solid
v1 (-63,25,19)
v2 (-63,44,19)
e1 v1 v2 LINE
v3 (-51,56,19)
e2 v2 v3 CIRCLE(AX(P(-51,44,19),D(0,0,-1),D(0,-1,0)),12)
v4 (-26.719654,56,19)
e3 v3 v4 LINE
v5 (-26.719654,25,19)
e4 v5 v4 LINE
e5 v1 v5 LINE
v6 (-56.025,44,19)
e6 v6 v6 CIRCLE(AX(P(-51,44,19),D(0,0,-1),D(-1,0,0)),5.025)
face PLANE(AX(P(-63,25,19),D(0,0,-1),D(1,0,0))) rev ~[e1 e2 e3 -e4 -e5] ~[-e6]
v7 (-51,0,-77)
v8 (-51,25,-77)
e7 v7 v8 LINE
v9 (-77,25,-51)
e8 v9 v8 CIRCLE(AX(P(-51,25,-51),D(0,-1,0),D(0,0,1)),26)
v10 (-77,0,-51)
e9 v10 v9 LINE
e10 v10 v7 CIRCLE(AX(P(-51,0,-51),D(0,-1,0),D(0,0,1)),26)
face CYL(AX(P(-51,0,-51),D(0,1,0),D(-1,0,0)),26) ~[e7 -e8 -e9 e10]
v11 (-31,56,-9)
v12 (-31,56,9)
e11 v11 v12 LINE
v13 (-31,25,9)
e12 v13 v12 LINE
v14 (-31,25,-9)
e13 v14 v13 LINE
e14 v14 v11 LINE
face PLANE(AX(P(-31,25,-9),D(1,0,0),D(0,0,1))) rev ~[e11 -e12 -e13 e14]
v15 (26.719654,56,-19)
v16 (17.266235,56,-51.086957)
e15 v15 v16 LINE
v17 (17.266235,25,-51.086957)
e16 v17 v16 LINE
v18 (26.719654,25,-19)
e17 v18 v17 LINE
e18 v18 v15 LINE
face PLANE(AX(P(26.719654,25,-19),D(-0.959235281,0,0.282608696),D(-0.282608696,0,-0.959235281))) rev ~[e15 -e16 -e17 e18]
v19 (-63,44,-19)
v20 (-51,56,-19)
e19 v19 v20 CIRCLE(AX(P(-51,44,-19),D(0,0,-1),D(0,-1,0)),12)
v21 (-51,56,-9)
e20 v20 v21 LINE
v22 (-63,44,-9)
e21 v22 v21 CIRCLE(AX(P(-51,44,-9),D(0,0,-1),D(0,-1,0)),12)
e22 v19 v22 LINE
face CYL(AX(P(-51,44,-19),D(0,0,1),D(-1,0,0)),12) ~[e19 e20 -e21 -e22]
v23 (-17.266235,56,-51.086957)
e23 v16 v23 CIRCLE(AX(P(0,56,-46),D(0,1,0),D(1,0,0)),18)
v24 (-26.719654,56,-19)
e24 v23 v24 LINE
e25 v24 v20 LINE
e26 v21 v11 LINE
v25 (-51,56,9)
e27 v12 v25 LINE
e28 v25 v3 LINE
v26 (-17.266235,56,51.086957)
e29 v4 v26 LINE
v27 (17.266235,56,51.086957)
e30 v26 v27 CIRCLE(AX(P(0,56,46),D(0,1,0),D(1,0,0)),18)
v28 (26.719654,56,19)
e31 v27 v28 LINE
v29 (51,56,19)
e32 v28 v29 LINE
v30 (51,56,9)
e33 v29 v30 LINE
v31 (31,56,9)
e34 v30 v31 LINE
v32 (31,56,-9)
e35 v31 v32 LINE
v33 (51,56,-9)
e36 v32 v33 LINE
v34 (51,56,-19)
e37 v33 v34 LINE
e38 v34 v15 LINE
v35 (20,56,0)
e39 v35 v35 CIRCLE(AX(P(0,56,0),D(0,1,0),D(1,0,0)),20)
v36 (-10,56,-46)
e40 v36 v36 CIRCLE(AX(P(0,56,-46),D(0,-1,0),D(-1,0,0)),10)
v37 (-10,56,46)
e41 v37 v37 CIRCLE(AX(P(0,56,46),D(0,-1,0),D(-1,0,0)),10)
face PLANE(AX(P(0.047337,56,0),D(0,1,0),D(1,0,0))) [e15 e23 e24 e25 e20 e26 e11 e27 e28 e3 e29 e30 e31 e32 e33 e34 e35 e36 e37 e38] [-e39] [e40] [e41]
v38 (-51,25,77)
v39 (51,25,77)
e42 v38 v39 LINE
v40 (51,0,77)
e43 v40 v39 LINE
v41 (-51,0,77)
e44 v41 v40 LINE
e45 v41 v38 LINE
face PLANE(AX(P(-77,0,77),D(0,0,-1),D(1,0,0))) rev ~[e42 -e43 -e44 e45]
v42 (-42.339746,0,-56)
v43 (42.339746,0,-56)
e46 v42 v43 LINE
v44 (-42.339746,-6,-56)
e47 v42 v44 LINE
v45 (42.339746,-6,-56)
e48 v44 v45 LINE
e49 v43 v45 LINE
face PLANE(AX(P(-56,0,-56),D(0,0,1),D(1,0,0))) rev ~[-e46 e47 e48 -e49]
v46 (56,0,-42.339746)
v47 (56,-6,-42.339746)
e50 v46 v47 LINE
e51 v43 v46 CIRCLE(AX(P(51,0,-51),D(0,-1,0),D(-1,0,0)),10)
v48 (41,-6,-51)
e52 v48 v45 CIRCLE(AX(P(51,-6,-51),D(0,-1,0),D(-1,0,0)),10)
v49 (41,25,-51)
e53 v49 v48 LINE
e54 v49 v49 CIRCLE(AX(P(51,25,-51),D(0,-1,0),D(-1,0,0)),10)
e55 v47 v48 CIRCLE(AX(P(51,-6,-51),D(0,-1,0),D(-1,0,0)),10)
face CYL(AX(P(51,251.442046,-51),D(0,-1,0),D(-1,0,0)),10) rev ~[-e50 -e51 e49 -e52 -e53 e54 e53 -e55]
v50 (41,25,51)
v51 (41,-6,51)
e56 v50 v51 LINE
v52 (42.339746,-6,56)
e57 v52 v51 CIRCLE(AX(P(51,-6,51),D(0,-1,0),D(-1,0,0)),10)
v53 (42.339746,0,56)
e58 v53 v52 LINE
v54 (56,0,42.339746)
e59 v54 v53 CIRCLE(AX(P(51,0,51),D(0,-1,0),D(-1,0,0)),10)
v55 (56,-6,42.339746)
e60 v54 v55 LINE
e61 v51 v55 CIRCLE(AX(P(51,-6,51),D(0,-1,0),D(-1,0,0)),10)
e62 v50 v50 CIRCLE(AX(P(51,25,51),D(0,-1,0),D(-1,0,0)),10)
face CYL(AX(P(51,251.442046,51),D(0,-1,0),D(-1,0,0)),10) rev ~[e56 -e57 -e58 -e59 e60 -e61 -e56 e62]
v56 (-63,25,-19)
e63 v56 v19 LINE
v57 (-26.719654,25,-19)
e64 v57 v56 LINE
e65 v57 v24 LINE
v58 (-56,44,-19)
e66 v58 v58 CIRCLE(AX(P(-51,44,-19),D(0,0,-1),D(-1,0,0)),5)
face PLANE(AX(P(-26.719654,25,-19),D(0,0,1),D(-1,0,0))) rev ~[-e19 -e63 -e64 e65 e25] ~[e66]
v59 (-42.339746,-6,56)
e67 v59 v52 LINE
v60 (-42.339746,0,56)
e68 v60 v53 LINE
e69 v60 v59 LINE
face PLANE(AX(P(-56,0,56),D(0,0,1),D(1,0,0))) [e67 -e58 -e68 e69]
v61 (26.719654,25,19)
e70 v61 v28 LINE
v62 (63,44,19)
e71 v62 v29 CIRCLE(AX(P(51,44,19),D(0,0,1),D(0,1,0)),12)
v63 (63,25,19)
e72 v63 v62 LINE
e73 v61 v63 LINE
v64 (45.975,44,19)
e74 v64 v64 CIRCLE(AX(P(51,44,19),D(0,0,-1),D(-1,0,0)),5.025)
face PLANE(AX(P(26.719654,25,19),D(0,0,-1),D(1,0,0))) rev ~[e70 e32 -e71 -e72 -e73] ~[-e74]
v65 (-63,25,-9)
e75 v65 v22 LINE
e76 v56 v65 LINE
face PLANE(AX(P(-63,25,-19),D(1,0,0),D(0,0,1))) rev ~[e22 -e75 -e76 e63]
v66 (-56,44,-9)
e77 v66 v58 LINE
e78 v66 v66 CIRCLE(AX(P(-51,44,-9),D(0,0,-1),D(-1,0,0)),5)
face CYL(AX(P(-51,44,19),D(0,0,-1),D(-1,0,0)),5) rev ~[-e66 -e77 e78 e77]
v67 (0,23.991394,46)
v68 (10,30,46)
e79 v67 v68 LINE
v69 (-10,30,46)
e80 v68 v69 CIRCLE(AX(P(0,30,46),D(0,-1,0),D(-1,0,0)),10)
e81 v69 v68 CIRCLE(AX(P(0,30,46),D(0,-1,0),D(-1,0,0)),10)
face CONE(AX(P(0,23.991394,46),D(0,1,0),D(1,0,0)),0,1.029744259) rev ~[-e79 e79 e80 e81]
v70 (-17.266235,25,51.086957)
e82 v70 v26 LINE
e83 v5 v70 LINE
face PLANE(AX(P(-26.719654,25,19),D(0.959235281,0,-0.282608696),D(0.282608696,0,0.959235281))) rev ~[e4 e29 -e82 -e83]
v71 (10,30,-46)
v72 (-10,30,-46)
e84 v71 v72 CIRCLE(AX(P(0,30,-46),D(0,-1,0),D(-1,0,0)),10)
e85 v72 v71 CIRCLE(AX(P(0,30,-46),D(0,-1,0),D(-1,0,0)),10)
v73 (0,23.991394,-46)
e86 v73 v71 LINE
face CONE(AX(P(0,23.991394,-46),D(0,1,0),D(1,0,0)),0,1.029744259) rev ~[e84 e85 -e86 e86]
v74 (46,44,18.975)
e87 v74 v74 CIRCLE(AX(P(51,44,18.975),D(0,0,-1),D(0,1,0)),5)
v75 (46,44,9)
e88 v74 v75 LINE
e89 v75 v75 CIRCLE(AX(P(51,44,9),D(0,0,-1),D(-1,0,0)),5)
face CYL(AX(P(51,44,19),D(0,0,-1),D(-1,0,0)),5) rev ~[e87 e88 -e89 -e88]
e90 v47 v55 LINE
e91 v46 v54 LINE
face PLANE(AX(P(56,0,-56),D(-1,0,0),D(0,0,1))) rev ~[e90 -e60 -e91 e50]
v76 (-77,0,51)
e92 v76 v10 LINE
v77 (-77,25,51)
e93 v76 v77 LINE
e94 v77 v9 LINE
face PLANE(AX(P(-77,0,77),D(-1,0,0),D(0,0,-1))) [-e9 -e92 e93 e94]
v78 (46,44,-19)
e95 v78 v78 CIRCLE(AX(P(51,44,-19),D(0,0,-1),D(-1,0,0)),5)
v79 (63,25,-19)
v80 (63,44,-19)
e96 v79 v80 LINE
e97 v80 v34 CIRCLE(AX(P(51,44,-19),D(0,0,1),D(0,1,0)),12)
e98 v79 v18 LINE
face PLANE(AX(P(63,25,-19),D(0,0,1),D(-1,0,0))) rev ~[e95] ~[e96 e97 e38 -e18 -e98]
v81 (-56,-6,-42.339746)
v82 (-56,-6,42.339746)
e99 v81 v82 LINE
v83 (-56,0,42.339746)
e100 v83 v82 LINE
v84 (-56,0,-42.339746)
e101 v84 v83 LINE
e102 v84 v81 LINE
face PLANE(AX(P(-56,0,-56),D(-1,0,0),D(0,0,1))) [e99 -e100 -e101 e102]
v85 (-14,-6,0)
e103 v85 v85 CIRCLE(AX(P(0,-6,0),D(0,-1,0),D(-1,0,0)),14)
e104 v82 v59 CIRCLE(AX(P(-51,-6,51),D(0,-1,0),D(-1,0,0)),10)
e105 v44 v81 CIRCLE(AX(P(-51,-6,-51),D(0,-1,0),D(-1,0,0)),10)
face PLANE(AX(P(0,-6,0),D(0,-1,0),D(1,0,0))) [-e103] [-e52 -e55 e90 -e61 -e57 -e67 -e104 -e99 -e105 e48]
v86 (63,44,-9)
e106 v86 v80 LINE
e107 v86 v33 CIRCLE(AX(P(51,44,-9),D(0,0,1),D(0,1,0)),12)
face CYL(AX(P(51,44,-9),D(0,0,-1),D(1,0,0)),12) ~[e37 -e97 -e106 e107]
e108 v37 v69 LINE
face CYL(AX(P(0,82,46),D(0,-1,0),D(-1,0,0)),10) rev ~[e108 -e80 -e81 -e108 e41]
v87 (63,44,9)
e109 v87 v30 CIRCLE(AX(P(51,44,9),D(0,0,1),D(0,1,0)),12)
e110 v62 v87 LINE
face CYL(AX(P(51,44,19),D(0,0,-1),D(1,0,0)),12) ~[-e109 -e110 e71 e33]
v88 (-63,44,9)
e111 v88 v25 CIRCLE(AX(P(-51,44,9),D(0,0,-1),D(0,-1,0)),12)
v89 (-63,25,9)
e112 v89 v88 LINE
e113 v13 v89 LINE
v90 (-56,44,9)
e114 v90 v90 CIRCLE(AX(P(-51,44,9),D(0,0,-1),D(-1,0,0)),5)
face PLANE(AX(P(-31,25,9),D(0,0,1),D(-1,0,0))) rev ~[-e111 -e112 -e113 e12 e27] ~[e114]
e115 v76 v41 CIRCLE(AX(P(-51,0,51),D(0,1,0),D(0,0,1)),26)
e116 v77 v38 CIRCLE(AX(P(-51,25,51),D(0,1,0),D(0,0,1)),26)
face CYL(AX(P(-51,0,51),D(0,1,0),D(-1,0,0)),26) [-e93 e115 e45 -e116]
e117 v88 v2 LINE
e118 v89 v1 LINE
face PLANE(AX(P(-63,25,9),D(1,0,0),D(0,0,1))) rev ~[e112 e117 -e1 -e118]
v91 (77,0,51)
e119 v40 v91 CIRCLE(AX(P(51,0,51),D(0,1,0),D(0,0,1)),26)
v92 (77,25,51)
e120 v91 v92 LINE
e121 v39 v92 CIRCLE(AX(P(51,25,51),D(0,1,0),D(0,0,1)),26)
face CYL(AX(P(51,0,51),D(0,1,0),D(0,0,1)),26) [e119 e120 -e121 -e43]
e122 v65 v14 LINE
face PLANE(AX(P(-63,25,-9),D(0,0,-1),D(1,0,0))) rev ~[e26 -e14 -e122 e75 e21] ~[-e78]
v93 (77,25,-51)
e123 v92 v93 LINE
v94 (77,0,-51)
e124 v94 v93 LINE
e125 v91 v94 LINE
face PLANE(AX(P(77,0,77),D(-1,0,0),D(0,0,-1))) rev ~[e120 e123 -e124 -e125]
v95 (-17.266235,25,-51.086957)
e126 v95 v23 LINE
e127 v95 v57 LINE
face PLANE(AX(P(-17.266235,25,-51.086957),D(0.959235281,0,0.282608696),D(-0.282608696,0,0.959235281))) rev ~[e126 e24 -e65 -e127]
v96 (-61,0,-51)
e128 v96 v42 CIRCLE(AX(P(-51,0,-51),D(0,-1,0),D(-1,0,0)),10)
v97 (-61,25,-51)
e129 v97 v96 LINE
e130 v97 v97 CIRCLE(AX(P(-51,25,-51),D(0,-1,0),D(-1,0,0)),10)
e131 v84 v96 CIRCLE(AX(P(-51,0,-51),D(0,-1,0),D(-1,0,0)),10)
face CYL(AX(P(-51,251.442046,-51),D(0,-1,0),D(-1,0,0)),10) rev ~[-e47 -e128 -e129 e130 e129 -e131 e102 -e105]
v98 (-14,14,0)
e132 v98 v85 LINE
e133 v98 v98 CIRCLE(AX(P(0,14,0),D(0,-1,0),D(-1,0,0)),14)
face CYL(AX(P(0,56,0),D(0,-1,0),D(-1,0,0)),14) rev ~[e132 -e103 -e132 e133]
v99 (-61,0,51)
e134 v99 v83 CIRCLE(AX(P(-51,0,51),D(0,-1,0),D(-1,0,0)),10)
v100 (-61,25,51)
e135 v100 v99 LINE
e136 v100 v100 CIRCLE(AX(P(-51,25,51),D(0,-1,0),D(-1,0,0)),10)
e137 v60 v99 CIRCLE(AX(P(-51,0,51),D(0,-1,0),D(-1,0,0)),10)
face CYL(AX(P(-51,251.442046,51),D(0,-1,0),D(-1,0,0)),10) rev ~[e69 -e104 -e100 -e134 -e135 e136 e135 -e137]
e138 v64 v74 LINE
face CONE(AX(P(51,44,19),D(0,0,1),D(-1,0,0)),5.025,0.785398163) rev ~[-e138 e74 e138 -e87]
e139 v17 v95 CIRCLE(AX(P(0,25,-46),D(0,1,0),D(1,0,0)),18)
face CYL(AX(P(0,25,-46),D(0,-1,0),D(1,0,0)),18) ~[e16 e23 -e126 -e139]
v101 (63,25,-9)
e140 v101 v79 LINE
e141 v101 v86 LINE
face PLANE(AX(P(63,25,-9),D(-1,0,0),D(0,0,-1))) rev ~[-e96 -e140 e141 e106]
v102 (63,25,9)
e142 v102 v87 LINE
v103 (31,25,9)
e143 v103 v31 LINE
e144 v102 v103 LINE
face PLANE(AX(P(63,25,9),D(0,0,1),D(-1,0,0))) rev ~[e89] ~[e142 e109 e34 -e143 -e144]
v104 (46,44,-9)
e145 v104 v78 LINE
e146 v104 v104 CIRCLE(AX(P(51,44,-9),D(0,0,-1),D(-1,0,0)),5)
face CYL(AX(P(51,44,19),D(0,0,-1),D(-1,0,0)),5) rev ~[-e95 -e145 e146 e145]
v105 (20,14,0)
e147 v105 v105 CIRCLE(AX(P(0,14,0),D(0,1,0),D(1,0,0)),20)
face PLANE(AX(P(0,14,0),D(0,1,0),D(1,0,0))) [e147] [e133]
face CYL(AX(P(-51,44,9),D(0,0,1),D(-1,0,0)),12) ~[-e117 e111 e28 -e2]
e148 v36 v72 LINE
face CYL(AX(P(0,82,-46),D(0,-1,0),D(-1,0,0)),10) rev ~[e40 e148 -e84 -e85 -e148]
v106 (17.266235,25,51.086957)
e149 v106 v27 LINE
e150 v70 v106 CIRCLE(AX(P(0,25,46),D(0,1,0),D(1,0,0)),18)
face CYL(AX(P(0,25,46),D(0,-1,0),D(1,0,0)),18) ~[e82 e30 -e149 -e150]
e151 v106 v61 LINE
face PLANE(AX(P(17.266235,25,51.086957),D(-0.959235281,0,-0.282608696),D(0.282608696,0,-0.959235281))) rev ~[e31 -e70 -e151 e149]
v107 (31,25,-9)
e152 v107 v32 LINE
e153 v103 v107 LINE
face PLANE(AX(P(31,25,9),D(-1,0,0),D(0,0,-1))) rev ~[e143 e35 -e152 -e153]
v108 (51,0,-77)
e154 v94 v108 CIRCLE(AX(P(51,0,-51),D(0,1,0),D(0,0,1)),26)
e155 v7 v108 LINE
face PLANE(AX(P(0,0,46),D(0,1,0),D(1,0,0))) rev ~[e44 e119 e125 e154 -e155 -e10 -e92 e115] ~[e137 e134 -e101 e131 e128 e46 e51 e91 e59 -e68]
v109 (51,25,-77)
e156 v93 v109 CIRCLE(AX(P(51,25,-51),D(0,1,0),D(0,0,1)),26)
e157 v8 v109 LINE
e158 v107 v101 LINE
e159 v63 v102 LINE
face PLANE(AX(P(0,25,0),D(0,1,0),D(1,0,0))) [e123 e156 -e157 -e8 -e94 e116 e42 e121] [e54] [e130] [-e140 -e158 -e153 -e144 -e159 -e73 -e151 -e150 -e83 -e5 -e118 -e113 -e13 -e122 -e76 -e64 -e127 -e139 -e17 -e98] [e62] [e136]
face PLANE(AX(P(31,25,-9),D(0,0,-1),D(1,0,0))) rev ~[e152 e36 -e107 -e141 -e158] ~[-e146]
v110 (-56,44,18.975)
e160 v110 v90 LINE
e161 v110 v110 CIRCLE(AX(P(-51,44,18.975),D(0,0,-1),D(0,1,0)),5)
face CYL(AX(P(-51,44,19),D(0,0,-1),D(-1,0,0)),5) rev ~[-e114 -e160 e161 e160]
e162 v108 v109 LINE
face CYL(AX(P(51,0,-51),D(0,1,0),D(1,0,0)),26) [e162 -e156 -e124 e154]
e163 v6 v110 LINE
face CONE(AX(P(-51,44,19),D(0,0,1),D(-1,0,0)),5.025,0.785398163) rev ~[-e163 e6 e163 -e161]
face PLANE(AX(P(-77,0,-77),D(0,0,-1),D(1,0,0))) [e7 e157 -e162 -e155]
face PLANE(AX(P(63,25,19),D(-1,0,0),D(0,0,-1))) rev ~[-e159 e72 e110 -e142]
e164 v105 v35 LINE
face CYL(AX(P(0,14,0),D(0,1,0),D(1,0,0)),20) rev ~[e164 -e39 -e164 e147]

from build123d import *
from OCP.BRepFilletAPI import BRepFilletAPI_MakeFillet

# Parameters (mm, degrees)
PLATE_AND_BOSS_PROFILE_W             = 154
PLATE_AND_BOSS_PROFILE_H             = 154
PLATE_AND_BOSS_PROFILE_R             = 18
BASE_PLATE_DEPTH                     = 25
CENTRAL_START                        = 25
SKETCH1_3_R                          = 18
CENTRAL_BOSS_AND_LUGS_DEPTH          = 31
PLATE_AND_BOSS_FILLETS_R26_R12_R1    = 12
PLATE_AND_BOSS_FILLETS_R26_R12_R2    = 26
LUG_PIN_HOLES_10_D                   = 10
LUG_PIN_HOLES_10_CSINK_D             = 10.05
LUG_PIN_HOLES_10_CSINK_ANGLE         = 90
LOCATING_SPIGOT_PROFILE_112_W        = 112
LOCATING_SPIGOT_PROFILE_112_H        = 112
LOCATING_SPIGOT_DEPTH                = 6
CENTRAL_BORE_28_CBORE_40_D           = 28
CENTRAL_BORE_28_CBORE_40_CBORE_D     = 40
CENTRAL_BORE_28_CBORE_40_CBORE_DEPTH = 42
PLATE_MOUNTING_HOLES_20_D            = 20
BOSS_TAPPED_HOLES_M22X2_0_D          = 20
BOSS_TAPPED_HOLES_M22X2_0_DEPTH      = 26
BOSS_TAPPED_HOLES_M22X2_0_TIP        = 6.00860619


with BuildPart() as part:
    # Plate and Boss Profile → Base Plate (new body)
    # profile 1 of 4: a face of its own
    with BuildSketch(Plane(origin=(0, 0, 0), x_dir=(1, 0, 0), z_dir=(0, 1, 0))):
        Rectangle(PLATE_AND_BOSS_PROFILE_W, PLATE_AND_BOSS_PROFILE_H)
        with BuildLine():
            Line((-26.719653956, 19), (-17.266235066, 51.086956522))
            ThreePointArc((-17.266235066, 51.086956522), (0, 64), (17.266235066, 51.086956522))
            Line((17.266235066, 51.086956522), (26.719653956, 19))
            Line((26.719653956, 19), (63, 19))
            Line((63, 19), (63, 9))
            Line((63, 9), (31, 9))
            Line((31, 9), (31, -9))
            Line((31, -9), (63, -9))
            Line((63, -9), (63, -19))
            Line((63, -19), (26.719653956, -19))
            Line((26.719653956, -19), (17.266235066, -51.086956522))
            ThreePointArc((17.266235066, -51.086956522), (0, -64), (-17.266235066, -51.086956522))
            Line((-17.266235066, -51.086956522), (-26.719653956, -19))
            Line((-26.719653956, -19), (-63, -19))
            Line((-63, -19), (-63, -9))
            Line((-63, -9), (-31, -9))
            Line((-31, -9), (-31, 9))
            Line((-31, 9), (-63, 9))
            Line((-63, 9), (-63, 19))
            Line((-63, 19), (-26.719653956, 19))
        make_face(mode=Mode.SUBTRACT)
    # profile 2 of 4: a face of its own
    with BuildSketch(Plane(origin=(0, 0, 0), x_dir=(1, 0, 0), z_dir=(0, 1, 0))):
        with BuildLine():
            ThreePointArc((18, 46), (-2.569802406, 28.184385624), (-17.266235066, 51.086956522))
            Line((-17.266235066, 51.086956522), (-26.719653956, 19))
            Line((-26.719653956, 19), (-63, 19))
            Line((-63, 19), (-63, 9))
            Line((-63, 9), (-31, 9))
            Line((-31, 9), (-31, -9))
            Line((-31, -9), (-63, -9))
            Line((-63, -9), (-63, -19))
            Line((-63, -19), (-26.719653956, -19))
            Line((-26.719653956, -19), (-17.266235066, -51.086956522))
            ThreePointArc((-17.266235066, -51.086956522), (-2.569802406, -28.184385624), (18, -46))
            ThreePointArc((18, -46), (17.815614376, -48.569802406), (17.266235066, -51.086956522))
            Line((17.266235066, -51.086956522), (26.719653956, -19))
            Line((26.719653956, -19), (63, -19))
            Line((63, -19), (63, -9))
            Line((63, -9), (31, -9))
            Line((31, -9), (31, 9))
            Line((31, 9), (63, 9))
            Line((63, 9), (63, 19))
            Line((63, 19), (26.719653956, 19))
            Line((26.719653956, 19), (17.266235066, 51.086956522))
            ThreePointArc((17.266235066, 51.086956522), (17.815614376, 48.569802406), (18, 46))
        make_face()
    # profile 3 of 4: a face of its own
    with BuildSketch(Plane(origin=(0, 0, 0), x_dir=(1, 0, 0), z_dir=(0, 1, 0))):
        with Locations((0, 46)):
            Circle(PLATE_AND_BOSS_PROFILE_R)
    # profile 4 of 4: a face of its own
    with BuildSketch(Plane(origin=(0, 0, 0), x_dir=(1, 0, 0), z_dir=(0, 1, 0))):
        with Locations((0, -46)):
            Circle(PLATE_AND_BOSS_PROFILE_R)
    extrude(amount=BASE_PLATE_DEPTH)

    # Sketch1_3 → Central Boss and Lugs (add)
    with BuildSketch(Plane(origin=(0, 0, 0), x_dir=(1, 0, 0), z_dir=(0, 1, 0)).offset(CENTRAL_START)):
        with BuildLine():
            ThreePointArc((18, 46), (-2.569802406, 28.184385624), (-17.266235066, 51.086956522))
            Line((-17.266235066, 51.086956522), (-26.719653956, 19))
            Line((-26.719653956, 19), (-63, 19))
            Line((-63, 19), (-63, 9))
            Line((-63, 9), (-31, 9))
            Line((-31, 9), (-31, -9))
            Line((-31, -9), (-63, -9))
            Line((-63, -9), (-63, -19))
            Line((-63, -19), (-26.719653956, -19))
            Line((-26.719653956, -19), (-17.266235066, -51.086956522))
            ThreePointArc((-17.266235066, -51.086956522), (-2.569802406, -28.184385624), (18, -46))
            ThreePointArc((18, -46), (17.815614376, -48.569802406), (17.266235066, -51.086956522))
            Line((17.266235066, -51.086956522), (26.719653956, -19))
            Line((26.719653956, -19), (63, -19))
            Line((63, -19), (63, -9))
            Line((63, -9), (31, -9))
            Line((31, -9), (31, 9))
            Line((31, 9), (63, 9))
            Line((63, 9), (63, 19))
            Line((63, 19), (26.719653956, 19))
            Line((26.719653956, 19), (17.266235066, 51.086956522))
            ThreePointArc((17.266235066, 51.086956522), (17.815614376, 48.569802406), (18, 46))
        make_face()
        with Locations((0, 46)):
            Circle(SKETCH1_3_R)
        with Locations((0, -46)):
            Circle(SKETCH1_3_R)
    extrude(amount=CENTRAL_BOSS_AND_LUGS_DEPTH)

    # Plate and Boss Fillets R26 R12: one fillet with a radius per group of edges: ONE call of the kernel's fillet builder (fillet() takes one radius for all edges)
    plate_and_boss_fillets_r26_r12_edges_1 = [part.edges().sort_by_distance(p)[0] for p in [
        (63, 56, 14),
        (-63, 56, -14),
        (63, 56, -14),
        (-63, 56, 14),
    ]]
    plate_and_boss_fillets_r26_r12_edges_2 = [part.edges().sort_by_distance(p)[0] for p in [
        (77, 12.5, 77),
        (-77, 12.5, 77),
        (-77, 12.5, -77),
        (77, 12.5, -77),
    ]]
    plate_and_boss_fillets_r26_r12 = BRepFilletAPI_MakeFillet(part.part.solid().wrapped)
    for e in plate_and_boss_fillets_r26_r12_edges_1:
        plate_and_boss_fillets_r26_r12.Add(PLATE_AND_BOSS_FILLETS_R26_R12_R1, e.wrapped)
    for e in plate_and_boss_fillets_r26_r12_edges_2:
        plate_and_boss_fillets_r26_r12.Add(PLATE_AND_BOSS_FILLETS_R26_R12_R2, e.wrapped)
    add(Compound.cast(plate_and_boss_fillets_r26_r12.Shape()), mode=Mode.REPLACE)

    # Lug Pin Holes _10 (through all)
    with Locations(Plane.XY.offset(19)):
        with Locations((-51, 44), (51, 44)):
            CounterSinkHole(LUG_PIN_HOLES_10_D / 2, LUG_PIN_HOLES_10_CSINK_D / 2, counter_sink_angle=LUG_PIN_HOLES_10_CSINK_ANGLE)

    # Locating Spigot Profile _112 → Locating Spigot (add)
    with BuildSketch(Plane.XZ):
        Rectangle(LOCATING_SPIGOT_PROFILE_112_W, LOCATING_SPIGOT_PROFILE_112_H)
    extrude(amount=LOCATING_SPIGOT_DEPTH)

    # Central Bore _28 Cbore _40 (through all)
    with Locations(Plane(origin=(0, 56, 0), x_dir=(1, 0, 0), z_dir=(0, 1, 0))):
        with Locations((0, 0)):
            CounterBoreHole(CENTRAL_BORE_28_CBORE_40_D / 2, CENTRAL_BORE_28_CBORE_40_CBORE_D / 2, CENTRAL_BORE_28_CBORE_40_CBORE_DEPTH)

    # Plate Mounting Holes _20 (through all)
    with Locations(Plane(origin=(0, 25, 0), x_dir=(1, 0, 0), z_dir=(0, 1, 0))):
        with Locations((51, -51), (51, 51), (-51, 51), (-51, -51)):
            Hole(PLATE_MOUNTING_HOLES_20_D / 2)

    # Boss Tapped Holes M22x2.0
    with Locations(Plane(origin=(0, 56, 0), x_dir=(1, 0, 0), z_dir=(0, 1, 0))):
        with Locations((0, -46), (0, 46)):
            Hole(BOSS_TAPPED_HOLES_M22X2_0_D / 2, depth=BOSS_TAPPED_HOLES_M22X2_0_DEPTH)
            with Locations((0, 0, -(BOSS_TAPPED_HOLES_M22X2_0_DEPTH + BOSS_TAPPED_HOLES_M22X2_0_TIP / 2))):  # 118° drill point
                Cone(0, BOSS_TAPPED_HOLES_M22X2_0_D / 2, BOSS_TAPPED_HOLES_M22X2_0_TIP, mode=Mode.SUBTRACT)


solid = part.part
